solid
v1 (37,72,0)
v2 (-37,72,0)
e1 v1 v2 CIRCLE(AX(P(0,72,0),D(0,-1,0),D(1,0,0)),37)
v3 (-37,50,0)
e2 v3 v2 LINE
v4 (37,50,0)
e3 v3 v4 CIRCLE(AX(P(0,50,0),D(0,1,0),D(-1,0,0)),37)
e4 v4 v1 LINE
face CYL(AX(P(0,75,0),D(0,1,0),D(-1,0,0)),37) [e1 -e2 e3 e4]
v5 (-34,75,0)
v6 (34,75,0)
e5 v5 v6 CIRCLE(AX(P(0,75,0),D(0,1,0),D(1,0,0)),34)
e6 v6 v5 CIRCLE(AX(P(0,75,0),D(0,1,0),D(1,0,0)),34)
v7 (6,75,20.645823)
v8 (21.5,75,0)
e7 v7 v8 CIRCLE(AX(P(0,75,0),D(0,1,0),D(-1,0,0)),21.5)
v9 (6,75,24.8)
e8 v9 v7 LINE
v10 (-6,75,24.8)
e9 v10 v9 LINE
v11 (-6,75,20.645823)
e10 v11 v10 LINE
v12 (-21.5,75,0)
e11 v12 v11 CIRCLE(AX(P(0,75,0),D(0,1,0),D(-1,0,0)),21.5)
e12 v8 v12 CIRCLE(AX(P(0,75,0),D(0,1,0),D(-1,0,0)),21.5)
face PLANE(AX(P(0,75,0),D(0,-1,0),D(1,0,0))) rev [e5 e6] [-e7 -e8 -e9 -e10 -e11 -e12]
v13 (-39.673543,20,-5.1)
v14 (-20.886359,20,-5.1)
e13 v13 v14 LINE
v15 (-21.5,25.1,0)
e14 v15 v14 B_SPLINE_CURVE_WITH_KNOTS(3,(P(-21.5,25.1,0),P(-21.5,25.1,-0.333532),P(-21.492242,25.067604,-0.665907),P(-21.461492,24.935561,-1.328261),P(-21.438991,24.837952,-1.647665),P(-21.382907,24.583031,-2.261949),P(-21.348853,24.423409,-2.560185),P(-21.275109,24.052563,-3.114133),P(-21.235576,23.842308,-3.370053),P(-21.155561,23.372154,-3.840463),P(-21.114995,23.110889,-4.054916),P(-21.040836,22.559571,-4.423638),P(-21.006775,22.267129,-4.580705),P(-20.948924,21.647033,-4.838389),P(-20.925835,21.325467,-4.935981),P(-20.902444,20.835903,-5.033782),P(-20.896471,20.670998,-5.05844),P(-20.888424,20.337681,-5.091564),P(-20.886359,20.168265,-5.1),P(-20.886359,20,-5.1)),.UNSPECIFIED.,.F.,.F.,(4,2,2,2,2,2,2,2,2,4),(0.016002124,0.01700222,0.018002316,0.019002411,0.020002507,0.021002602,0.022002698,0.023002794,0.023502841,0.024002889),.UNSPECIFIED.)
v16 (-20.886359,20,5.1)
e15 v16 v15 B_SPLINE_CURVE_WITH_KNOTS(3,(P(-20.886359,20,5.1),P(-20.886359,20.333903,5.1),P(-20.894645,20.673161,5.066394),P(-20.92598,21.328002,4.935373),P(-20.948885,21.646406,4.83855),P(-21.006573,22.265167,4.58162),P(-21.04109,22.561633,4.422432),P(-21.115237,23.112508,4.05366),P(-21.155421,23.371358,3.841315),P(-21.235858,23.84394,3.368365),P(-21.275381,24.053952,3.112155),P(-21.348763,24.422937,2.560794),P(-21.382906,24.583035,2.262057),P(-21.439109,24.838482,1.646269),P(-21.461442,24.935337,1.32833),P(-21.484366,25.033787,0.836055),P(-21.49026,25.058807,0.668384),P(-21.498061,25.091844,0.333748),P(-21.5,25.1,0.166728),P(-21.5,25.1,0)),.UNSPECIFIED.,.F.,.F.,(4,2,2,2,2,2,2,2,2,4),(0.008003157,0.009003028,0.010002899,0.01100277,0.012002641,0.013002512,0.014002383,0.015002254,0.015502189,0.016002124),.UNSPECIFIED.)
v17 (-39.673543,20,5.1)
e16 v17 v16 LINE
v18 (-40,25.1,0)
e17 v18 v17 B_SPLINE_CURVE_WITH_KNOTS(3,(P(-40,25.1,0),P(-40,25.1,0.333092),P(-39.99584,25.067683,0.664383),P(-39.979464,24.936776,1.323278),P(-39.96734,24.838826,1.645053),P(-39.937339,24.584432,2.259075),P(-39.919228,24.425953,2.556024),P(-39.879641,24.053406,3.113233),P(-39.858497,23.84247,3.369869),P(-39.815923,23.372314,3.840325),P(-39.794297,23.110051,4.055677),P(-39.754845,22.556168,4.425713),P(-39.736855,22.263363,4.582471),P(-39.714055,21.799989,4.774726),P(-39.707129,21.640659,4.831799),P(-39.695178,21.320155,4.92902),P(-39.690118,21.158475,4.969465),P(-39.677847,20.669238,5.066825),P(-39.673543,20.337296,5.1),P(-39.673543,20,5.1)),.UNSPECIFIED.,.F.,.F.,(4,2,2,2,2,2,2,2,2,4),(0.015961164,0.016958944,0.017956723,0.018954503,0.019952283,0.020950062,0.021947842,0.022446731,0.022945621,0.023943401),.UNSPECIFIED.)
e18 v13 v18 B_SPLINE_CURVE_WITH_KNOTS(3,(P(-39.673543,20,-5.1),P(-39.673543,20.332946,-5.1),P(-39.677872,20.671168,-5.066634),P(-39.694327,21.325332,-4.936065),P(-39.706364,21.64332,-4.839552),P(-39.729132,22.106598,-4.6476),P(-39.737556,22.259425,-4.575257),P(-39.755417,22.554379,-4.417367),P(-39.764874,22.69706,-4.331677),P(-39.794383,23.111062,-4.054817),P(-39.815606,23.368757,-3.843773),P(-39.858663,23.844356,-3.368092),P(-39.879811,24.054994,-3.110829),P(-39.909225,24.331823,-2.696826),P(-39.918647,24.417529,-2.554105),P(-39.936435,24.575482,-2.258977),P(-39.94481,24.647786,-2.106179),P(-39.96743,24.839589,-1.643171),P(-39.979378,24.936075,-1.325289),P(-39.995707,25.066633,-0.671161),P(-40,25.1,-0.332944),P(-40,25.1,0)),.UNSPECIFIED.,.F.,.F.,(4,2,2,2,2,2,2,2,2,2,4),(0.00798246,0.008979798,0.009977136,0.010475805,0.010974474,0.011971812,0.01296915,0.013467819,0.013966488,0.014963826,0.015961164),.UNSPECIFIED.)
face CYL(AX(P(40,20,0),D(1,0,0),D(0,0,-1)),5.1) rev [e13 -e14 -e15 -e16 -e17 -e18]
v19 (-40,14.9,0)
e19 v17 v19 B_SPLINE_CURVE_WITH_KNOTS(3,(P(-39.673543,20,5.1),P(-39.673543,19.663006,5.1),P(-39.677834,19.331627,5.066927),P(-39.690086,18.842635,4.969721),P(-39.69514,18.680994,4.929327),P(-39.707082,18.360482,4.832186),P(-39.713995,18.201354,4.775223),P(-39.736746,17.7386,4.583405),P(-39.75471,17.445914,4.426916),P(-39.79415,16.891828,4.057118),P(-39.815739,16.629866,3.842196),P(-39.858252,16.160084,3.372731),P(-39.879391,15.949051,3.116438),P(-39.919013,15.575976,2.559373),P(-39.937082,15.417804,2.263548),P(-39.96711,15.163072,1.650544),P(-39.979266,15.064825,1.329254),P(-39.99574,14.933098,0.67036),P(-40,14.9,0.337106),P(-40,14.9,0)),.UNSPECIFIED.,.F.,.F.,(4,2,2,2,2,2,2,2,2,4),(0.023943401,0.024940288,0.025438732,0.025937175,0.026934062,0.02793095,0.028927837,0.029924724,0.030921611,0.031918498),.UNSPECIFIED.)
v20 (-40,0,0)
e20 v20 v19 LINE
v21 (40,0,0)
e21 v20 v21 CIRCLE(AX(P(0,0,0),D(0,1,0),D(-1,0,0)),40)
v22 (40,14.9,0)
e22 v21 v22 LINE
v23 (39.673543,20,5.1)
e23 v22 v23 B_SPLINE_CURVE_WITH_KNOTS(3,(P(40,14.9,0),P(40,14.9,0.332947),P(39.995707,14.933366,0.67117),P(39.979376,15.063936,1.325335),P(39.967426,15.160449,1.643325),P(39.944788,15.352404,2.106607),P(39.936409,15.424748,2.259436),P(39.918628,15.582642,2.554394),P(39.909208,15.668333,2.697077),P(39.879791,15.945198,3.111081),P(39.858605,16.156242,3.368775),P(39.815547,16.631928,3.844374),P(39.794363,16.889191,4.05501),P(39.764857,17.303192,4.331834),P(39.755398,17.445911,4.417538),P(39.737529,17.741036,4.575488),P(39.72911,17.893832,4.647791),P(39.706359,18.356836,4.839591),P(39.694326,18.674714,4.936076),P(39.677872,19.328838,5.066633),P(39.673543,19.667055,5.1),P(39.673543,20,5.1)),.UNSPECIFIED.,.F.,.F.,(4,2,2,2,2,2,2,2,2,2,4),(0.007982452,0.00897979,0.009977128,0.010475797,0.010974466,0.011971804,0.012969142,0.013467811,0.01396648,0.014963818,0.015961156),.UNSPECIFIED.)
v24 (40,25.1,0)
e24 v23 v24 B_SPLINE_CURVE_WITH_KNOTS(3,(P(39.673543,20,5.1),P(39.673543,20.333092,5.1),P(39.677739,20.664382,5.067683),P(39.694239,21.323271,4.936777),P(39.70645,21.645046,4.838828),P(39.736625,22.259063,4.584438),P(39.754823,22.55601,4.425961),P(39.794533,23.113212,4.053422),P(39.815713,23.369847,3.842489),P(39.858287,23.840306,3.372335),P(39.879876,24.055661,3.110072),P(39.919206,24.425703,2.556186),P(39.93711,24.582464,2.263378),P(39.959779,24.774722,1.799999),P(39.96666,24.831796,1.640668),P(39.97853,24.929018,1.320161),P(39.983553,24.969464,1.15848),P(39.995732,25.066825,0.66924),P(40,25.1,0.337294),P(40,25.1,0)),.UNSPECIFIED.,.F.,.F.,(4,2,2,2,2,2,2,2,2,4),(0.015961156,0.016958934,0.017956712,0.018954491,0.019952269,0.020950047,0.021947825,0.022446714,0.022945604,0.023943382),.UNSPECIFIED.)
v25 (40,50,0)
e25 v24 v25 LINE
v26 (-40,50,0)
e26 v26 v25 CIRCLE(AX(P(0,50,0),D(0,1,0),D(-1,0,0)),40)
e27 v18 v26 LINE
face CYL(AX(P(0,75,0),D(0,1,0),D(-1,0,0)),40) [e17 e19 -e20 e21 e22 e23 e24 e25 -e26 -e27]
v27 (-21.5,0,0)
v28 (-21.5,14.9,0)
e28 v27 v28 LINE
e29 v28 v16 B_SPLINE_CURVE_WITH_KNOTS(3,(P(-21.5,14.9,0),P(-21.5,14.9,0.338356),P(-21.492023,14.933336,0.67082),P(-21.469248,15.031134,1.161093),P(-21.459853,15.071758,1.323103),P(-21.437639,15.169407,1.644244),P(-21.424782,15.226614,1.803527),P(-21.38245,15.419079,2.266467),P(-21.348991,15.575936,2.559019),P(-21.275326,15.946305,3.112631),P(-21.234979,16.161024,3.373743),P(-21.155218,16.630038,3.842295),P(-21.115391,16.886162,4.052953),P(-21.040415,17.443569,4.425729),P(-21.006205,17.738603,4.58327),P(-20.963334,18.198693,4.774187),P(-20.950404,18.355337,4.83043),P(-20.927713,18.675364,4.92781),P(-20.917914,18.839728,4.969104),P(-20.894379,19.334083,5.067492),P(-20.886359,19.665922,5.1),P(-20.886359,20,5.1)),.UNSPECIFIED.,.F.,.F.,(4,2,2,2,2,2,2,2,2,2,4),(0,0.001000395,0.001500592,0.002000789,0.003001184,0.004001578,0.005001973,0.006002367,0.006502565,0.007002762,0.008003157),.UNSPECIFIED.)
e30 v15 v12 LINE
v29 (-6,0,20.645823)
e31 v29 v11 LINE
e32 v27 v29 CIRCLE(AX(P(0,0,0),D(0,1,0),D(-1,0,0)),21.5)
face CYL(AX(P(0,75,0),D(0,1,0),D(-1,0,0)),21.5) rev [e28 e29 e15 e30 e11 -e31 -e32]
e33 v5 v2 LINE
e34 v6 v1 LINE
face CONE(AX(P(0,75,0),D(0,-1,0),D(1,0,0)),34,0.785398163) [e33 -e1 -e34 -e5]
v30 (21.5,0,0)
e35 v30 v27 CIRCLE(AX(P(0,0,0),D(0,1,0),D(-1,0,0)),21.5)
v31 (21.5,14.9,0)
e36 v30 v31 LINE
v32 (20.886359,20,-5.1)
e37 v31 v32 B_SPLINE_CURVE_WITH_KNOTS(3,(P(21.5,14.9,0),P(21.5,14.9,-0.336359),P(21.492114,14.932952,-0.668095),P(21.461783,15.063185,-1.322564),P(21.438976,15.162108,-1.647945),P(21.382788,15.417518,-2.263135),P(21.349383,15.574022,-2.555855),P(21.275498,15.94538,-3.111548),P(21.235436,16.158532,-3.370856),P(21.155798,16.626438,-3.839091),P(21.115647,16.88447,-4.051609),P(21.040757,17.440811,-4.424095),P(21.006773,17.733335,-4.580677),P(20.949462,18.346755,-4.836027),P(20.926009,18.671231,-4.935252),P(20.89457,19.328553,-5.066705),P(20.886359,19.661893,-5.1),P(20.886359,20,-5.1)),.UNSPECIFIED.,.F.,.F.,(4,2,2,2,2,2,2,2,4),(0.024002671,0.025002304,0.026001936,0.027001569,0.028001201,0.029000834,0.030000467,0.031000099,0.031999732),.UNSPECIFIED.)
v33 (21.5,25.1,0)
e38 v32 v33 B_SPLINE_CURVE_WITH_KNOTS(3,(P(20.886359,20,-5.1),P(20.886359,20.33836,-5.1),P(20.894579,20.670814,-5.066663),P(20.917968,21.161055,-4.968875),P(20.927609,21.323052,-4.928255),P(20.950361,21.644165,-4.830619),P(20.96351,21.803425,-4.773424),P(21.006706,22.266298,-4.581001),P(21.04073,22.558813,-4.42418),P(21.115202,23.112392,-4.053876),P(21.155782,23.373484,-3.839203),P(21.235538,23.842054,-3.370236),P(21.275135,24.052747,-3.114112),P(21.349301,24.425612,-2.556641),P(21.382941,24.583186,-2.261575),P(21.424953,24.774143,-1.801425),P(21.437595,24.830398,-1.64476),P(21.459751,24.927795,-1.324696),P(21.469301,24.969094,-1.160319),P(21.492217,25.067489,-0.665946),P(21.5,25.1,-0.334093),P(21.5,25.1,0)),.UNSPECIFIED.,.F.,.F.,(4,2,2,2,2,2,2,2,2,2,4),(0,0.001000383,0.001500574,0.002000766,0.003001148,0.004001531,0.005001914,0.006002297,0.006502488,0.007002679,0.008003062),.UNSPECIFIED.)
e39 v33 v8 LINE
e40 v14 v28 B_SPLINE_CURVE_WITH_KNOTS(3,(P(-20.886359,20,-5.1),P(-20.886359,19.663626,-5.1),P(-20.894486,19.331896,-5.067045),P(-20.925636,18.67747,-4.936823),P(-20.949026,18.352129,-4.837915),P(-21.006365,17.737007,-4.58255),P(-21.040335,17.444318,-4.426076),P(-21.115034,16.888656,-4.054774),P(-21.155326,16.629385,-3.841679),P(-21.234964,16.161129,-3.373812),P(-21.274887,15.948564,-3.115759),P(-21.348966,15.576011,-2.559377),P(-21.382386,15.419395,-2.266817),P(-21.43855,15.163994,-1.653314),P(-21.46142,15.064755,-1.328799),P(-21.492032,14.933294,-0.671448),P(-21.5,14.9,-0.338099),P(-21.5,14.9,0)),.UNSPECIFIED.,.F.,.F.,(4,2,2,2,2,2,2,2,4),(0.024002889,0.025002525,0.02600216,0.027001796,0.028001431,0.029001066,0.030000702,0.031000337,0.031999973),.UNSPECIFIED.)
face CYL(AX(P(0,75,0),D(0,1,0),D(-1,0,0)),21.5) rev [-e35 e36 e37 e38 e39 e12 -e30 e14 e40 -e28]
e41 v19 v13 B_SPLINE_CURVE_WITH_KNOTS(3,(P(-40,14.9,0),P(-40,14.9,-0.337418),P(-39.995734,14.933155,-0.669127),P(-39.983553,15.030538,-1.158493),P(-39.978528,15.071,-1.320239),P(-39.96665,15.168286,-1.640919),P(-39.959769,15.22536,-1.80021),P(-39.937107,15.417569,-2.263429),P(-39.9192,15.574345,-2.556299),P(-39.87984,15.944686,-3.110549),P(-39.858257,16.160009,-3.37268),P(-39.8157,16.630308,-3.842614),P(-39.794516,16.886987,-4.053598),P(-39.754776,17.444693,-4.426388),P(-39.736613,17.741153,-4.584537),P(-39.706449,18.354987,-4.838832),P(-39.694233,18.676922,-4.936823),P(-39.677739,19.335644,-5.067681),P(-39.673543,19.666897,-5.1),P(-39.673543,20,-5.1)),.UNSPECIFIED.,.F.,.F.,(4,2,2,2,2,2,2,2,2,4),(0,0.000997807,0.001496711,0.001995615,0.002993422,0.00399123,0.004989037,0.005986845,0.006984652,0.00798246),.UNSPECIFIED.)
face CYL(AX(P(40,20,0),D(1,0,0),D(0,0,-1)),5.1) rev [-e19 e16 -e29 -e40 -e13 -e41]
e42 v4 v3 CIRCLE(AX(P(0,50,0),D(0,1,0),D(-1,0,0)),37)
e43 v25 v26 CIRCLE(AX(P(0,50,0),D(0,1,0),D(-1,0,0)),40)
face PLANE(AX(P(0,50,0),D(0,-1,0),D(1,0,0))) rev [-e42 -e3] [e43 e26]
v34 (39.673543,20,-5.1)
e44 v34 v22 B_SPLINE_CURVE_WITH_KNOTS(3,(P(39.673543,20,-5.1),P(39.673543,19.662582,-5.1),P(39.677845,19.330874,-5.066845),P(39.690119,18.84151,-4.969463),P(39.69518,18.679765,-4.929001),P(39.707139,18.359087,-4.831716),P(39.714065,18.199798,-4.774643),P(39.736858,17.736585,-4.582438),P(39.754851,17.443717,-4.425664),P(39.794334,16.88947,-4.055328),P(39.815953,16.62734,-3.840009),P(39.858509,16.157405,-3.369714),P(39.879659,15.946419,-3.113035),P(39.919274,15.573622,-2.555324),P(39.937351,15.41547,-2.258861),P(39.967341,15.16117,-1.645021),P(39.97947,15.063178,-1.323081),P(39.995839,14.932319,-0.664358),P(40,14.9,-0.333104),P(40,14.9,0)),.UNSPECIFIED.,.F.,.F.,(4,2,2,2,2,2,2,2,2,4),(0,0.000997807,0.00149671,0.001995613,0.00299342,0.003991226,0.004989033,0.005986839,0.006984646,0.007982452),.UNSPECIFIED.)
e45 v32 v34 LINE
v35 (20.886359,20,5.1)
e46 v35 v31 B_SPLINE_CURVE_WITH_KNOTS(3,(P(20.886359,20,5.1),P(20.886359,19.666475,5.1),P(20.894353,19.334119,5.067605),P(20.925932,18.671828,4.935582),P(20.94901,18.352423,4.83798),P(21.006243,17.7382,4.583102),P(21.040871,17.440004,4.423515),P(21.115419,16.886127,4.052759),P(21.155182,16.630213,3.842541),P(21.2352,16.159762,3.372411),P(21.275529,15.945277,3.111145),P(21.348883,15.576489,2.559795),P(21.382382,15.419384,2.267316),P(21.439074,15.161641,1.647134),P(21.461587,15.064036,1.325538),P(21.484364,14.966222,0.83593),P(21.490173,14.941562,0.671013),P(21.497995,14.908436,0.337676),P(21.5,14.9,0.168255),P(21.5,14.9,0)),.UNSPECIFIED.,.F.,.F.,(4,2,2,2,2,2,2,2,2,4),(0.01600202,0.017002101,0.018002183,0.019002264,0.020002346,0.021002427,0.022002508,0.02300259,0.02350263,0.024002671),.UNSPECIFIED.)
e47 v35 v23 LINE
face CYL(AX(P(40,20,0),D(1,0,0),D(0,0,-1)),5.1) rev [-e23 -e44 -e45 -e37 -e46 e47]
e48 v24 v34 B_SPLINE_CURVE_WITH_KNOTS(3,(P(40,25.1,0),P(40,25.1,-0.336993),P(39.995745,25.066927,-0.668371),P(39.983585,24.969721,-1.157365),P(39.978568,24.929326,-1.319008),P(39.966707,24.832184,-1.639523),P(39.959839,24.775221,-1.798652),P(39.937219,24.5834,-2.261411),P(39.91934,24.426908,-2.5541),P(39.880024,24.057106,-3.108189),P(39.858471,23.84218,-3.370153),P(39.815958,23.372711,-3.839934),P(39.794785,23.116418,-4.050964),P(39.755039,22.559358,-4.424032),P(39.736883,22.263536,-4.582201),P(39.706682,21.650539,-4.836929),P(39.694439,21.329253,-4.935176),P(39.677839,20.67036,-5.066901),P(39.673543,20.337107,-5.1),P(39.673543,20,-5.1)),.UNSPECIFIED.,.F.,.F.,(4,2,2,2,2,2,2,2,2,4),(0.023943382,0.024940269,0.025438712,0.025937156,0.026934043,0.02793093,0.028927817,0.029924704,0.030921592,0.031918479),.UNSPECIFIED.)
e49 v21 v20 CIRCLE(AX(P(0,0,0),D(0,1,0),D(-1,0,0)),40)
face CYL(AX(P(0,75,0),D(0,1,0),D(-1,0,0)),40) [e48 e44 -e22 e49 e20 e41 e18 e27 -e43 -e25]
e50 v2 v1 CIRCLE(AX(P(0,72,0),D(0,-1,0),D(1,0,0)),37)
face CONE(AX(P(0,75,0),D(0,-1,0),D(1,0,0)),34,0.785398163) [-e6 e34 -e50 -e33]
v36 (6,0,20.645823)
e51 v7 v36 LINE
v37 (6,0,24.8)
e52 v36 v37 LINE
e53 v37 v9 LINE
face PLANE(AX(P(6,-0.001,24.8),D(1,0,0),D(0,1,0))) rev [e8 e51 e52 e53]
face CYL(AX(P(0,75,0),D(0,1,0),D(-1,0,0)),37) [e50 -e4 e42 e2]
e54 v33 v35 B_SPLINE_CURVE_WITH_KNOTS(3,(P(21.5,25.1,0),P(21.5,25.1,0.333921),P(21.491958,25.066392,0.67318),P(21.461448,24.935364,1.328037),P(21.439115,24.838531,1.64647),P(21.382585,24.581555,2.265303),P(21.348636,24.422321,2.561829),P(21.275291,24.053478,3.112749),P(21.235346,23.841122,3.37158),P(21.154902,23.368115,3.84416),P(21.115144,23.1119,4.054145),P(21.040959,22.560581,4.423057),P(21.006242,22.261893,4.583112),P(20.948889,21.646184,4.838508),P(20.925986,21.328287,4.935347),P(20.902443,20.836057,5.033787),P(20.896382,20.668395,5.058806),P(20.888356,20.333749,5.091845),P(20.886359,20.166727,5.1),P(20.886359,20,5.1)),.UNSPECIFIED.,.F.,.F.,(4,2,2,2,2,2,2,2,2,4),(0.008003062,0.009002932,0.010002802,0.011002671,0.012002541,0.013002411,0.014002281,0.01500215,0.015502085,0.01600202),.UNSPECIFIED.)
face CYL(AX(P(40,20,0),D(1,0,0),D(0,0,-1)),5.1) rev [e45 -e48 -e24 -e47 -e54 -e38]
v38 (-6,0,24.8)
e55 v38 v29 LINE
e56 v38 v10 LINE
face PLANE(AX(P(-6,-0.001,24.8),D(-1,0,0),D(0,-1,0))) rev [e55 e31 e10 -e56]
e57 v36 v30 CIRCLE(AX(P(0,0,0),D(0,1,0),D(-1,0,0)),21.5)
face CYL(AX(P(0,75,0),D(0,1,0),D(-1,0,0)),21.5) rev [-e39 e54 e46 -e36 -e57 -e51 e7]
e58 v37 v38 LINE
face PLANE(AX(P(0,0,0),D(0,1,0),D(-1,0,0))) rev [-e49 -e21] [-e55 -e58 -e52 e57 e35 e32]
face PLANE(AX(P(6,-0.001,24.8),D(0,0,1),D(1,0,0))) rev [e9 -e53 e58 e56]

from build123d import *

# Parameters (mm, degrees)
CHAMFER1_SIZE      = 3
M12_TAPPED_HOLE1_D = 10.2
CUT_EXTRUDE1_REACH = 95.941
SKETCH6_W          = 12
SKETCH6_H          = 6.6


with BuildPart() as part:
    # Sketch2 → Revolve1 (revolve)
    with BuildSketch(Plane.XY, mode=Mode.PRIVATE) as revolve1_sk:
        Polygon((21.5, 75), (21.5, 0), (40, 0), (40, 50), (37, 50), (37, 75), align=None)
    revolve(revolve1_sk.sketch.rotate(Axis((0, 75, 0), (0, -1, 0)), 180), axis=Axis((0, 75, 0), (0, -1, 0)))

    # Chamfer1
    chamfer1_edges = [part.edges().sort_by_distance(p)[0] for p in [
        (37, 75, 0),
    ]]
    chamfer(chamfer1_edges, length=CHAMFER1_SIZE)

    # M12 Tapped Hole1 (through all)
    with Locations(Plane(origin=(40, 0, 0), x_dir=(0, 0, -1), z_dir=(1, 0, 0))):
        with Locations((0, 20)):
            Hole(M12_TAPPED_HOLE1_D / 2)

    # Sketch6 → Cut-Extrude1 (cut, up to next)
    with BuildSketch(Plane(origin=(0, 75, 0), x_dir=(1, 0, 0), z_dir=(0, 1, 0)), mode=Mode.PRIVATE) as cut_extrude1_sk1:
        with Locations((0, -21.5)):
            Rectangle(SKETCH6_W, SKETCH6_H)
    cut_extrude1_tool1 = extrude(cut_extrude1_sk1.sketch, amount=-CUT_EXTRUDE1_REACH, mode=Mode.PRIVATE) & part.part
    add(cut_extrude1_tool1.solids().sort_by_distance((0, 75, 21.5))[0], mode=Mode.SUBTRACT)


solid = part.part
